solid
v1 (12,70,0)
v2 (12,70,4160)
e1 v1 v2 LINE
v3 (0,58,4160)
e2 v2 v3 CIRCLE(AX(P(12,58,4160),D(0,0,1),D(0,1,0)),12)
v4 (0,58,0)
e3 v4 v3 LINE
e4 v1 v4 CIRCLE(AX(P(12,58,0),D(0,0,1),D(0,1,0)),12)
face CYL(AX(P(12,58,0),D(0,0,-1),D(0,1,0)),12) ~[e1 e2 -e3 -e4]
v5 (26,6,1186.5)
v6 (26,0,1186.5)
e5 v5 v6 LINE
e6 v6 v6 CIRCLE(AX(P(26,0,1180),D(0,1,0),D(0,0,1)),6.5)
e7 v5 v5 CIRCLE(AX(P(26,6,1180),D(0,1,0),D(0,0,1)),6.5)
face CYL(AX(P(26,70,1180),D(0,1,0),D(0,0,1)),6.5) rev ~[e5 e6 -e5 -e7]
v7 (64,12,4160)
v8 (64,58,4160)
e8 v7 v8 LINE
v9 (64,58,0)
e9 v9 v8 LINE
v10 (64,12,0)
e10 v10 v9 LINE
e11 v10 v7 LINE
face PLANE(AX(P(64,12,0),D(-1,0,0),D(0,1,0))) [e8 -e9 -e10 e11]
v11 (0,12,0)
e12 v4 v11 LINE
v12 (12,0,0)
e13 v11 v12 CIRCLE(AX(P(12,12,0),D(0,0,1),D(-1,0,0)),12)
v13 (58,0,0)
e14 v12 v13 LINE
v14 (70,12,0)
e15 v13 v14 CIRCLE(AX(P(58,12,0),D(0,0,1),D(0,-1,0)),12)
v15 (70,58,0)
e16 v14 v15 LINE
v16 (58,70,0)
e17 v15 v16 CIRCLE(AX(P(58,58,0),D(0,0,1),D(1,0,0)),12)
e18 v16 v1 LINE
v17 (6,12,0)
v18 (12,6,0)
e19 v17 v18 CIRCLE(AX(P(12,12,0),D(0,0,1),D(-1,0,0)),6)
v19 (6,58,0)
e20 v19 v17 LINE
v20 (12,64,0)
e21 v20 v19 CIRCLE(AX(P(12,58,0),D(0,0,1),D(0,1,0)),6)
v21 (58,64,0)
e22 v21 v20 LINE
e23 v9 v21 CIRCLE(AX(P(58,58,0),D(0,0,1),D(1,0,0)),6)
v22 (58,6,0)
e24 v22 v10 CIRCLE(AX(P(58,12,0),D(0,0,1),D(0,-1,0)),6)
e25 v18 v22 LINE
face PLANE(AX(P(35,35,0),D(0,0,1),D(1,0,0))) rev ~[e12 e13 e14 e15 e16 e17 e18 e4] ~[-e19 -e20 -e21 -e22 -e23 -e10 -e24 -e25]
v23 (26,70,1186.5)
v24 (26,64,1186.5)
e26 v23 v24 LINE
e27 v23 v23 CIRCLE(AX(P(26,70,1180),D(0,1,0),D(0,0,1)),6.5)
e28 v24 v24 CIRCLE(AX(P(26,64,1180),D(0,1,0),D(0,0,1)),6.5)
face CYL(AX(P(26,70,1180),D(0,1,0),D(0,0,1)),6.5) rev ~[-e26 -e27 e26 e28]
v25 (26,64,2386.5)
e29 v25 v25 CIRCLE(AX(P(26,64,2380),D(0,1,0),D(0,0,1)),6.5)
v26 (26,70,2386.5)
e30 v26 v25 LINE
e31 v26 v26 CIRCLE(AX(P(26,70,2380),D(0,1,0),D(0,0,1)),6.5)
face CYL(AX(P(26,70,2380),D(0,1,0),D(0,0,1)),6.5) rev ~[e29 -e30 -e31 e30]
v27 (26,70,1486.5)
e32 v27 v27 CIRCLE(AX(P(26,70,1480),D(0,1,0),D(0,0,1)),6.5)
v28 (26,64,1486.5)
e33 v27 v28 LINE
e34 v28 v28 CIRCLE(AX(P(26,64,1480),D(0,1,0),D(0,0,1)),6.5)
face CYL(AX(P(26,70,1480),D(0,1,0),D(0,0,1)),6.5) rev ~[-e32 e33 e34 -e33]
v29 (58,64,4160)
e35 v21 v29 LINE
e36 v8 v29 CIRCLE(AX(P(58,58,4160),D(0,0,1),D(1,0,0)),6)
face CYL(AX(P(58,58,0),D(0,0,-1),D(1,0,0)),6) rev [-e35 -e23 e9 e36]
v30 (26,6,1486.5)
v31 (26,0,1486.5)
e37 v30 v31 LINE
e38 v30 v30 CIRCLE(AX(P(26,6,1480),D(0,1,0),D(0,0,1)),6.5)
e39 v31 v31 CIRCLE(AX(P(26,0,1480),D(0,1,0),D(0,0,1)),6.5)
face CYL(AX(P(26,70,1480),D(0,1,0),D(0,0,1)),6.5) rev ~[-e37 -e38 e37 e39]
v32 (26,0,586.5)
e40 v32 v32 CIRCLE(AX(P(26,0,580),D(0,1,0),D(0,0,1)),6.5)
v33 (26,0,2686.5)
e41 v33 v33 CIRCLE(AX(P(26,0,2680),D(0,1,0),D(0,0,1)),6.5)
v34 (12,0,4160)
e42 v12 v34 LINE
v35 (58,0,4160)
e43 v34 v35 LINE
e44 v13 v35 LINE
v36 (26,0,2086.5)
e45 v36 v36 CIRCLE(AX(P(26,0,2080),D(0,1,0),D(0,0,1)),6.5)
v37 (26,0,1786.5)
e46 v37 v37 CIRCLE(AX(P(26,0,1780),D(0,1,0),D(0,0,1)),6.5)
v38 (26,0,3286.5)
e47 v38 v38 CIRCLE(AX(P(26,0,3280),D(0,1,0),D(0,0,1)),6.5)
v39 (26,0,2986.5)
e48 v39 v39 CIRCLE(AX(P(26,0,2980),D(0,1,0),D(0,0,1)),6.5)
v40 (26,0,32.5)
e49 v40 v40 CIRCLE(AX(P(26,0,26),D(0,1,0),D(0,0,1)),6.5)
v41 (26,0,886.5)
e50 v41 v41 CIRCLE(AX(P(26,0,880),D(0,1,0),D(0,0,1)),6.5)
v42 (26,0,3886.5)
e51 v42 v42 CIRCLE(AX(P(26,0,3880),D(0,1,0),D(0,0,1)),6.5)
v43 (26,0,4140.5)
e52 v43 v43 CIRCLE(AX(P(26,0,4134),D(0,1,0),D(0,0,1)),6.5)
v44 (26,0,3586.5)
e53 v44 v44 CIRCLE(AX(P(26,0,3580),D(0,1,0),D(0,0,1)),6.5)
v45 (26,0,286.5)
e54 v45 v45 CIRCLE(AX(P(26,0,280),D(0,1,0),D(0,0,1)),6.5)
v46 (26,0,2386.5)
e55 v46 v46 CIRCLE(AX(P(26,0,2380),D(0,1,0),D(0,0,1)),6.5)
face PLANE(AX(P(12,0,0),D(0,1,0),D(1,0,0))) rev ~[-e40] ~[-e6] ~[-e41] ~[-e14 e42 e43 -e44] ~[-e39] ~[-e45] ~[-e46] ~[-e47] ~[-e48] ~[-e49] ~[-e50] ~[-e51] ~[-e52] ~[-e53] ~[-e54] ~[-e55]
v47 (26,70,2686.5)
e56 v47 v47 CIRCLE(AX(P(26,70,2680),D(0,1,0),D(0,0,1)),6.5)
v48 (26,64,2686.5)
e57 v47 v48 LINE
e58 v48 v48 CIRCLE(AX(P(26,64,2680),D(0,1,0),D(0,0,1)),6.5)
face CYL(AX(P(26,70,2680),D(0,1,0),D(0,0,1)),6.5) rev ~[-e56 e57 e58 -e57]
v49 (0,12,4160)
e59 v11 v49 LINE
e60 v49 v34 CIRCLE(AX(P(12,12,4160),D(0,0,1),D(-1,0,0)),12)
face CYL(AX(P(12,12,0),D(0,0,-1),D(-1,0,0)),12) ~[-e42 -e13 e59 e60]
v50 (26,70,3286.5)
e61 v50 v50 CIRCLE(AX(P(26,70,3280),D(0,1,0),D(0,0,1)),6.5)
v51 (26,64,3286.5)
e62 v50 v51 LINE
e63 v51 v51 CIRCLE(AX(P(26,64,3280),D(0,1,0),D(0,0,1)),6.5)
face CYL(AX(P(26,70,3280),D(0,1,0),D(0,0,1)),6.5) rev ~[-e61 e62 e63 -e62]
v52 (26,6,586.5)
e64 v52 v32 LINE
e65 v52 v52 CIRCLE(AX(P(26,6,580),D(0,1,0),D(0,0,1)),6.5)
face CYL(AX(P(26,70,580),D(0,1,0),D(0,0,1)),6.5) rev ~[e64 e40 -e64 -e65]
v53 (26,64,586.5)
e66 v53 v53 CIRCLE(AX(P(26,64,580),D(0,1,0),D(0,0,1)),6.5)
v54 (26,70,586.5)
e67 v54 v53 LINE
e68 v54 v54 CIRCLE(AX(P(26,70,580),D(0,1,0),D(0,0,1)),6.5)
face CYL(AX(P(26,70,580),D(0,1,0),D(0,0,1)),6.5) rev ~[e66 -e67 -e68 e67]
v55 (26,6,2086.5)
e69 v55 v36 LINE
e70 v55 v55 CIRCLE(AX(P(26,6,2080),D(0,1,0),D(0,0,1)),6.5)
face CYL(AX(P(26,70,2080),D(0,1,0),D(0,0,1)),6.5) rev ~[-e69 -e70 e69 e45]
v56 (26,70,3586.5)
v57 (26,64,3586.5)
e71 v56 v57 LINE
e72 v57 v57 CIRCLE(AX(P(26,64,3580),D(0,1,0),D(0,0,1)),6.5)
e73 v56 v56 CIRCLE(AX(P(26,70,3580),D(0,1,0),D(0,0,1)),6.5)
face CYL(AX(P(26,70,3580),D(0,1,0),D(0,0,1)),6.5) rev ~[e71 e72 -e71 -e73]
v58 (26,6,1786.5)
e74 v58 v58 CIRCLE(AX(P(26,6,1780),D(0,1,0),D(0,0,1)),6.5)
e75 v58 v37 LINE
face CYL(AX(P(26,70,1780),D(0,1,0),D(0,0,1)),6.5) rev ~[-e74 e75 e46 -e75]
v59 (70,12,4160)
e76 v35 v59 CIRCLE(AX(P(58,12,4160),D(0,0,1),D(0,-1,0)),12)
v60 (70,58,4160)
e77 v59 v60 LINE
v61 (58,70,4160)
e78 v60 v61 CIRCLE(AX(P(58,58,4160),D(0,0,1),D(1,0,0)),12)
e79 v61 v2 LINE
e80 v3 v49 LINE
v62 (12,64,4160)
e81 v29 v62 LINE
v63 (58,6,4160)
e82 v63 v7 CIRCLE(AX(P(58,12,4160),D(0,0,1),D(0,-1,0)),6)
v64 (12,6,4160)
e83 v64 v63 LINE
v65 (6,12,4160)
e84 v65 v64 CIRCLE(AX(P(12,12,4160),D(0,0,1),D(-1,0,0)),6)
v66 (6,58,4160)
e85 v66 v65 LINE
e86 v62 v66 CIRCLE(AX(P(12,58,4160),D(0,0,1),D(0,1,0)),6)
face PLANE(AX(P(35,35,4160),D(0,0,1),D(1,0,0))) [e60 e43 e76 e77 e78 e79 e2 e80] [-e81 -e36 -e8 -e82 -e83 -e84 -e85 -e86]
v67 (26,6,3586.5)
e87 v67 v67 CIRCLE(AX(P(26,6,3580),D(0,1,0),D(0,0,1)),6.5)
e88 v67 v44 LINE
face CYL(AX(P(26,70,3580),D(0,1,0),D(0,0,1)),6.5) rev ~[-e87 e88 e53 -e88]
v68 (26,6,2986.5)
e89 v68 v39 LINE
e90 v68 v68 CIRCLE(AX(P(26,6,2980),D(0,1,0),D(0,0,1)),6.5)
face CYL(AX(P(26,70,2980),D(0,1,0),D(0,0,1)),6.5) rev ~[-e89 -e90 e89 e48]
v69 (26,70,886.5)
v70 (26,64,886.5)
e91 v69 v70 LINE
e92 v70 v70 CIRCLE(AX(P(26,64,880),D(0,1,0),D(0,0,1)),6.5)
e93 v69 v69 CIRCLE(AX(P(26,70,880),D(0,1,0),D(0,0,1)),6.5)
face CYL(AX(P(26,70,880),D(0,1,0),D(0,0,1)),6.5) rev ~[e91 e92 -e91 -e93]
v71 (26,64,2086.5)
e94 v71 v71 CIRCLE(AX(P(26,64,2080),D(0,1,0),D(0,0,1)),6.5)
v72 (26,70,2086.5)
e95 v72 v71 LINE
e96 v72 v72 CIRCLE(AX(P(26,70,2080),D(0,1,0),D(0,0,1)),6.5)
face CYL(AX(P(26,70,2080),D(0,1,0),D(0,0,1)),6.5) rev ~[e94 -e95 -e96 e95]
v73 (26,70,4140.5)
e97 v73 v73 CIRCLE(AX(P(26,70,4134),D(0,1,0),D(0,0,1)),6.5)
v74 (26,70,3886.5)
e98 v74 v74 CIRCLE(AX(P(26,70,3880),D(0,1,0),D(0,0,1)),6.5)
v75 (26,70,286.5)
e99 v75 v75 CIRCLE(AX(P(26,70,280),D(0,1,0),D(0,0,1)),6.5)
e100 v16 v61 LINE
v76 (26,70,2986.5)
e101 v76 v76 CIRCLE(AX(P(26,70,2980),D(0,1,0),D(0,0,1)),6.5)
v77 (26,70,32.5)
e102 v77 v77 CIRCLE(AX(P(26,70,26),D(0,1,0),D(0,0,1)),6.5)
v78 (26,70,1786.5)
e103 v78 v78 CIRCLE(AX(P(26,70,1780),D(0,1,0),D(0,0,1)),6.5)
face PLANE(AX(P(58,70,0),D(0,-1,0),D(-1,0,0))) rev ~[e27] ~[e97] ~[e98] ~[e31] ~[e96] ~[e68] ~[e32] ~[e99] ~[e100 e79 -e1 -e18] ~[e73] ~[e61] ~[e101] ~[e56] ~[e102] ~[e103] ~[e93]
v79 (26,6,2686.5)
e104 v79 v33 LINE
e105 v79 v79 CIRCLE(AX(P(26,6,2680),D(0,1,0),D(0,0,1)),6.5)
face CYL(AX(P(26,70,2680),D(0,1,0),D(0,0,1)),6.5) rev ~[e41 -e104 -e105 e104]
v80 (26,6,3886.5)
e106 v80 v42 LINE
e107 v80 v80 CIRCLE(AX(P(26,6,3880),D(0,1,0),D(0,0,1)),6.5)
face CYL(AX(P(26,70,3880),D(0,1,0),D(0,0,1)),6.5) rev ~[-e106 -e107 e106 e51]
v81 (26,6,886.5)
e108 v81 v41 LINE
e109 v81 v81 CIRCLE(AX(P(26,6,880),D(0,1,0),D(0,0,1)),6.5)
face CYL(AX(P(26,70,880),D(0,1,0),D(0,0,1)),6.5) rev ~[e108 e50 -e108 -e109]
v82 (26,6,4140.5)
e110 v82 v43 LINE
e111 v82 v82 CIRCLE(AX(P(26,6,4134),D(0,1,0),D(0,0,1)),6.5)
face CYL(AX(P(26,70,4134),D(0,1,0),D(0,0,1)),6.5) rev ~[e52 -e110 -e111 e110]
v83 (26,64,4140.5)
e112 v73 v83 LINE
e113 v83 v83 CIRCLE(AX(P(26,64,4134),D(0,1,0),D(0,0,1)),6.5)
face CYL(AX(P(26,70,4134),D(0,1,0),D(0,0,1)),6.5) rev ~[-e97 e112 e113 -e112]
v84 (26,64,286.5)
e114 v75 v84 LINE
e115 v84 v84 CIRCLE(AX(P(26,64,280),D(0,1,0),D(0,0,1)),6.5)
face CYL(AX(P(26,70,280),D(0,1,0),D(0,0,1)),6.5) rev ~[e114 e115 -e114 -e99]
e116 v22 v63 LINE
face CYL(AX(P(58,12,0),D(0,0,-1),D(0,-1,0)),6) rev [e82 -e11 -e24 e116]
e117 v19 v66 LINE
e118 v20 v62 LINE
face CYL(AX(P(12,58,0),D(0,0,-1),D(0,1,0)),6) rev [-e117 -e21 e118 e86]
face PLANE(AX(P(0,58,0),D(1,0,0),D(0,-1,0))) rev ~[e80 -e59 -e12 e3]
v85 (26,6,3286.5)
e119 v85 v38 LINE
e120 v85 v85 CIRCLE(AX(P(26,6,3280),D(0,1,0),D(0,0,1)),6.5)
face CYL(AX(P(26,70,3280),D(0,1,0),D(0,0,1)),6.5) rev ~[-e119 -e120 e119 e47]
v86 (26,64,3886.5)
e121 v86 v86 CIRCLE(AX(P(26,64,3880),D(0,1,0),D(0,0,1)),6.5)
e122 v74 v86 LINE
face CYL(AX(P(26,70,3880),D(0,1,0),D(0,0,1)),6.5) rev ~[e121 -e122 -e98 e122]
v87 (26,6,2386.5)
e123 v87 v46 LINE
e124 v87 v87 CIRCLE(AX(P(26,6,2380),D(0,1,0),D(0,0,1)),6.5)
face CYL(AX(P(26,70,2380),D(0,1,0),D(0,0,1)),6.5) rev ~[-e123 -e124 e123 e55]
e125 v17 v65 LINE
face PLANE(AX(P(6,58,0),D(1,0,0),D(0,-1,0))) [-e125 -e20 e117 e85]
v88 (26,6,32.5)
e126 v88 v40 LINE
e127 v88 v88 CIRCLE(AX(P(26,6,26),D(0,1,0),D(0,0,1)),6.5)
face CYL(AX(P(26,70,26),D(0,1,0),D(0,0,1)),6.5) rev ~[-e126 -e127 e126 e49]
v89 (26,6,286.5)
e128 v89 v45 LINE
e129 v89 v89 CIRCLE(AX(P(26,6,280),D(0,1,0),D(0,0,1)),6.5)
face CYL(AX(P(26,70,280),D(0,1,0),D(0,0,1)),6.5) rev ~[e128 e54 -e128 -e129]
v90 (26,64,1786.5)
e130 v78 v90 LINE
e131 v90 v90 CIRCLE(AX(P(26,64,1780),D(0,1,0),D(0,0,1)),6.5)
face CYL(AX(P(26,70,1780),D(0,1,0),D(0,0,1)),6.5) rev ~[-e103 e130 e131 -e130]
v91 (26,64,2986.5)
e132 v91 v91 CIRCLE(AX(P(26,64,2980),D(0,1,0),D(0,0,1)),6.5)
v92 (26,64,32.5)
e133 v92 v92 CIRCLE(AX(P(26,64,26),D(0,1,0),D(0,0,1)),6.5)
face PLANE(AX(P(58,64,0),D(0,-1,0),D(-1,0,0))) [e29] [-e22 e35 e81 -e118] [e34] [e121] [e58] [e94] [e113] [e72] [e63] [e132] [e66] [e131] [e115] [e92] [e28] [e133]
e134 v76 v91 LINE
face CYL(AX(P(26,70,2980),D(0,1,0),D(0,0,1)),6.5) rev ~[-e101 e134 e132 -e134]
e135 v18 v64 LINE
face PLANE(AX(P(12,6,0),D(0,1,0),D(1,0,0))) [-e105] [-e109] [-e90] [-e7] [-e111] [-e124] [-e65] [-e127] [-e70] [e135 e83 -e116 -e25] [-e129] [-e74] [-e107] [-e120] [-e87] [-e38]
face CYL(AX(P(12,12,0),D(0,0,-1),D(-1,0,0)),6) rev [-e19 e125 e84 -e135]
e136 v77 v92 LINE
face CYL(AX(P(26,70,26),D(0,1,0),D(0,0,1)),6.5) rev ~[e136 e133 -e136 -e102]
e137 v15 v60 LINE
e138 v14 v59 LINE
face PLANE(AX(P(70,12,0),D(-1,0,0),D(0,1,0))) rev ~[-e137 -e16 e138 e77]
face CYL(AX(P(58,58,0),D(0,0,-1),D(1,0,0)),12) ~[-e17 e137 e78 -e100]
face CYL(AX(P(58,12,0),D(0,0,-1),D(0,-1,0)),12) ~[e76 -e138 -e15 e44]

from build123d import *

# Parameters (mm, degrees)
BOSS_EXTRUDE1_DEPTH = 4160
SKETCH2_R           = 6.5
CUT_EXTRUDE1_DEPTH  = 4162.177717906
SKETCH3_R           = 6.5
CUT_EXTRUDE2_DEPTH  = 4162.177717906


with BuildPart() as part:
    # Sketch1 → Boss-Extrude1 (new body)
    with BuildSketch(Plane.XY):
        with BuildLine():
            Line((12, 0), (58, 0))
            ThreePointArc((58, 0), (66.485281374, 3.514718626), (70, 12))
            Line((70, 12), (70, 58))
            ThreePointArc((70, 58), (66.485281374, 66.485281374), (58, 70))
            Line((58, 70), (12, 70))
            ThreePointArc((12, 70), (3.514718626, 66.485281374), (0, 58))
            Line((0, 58), (0, 12))
            ThreePointArc((0, 12), (3.514718626, 3.514718626), (12, 0))
        make_face()
        with BuildLine():
            Line((12, 6), (58, 6))
            ThreePointArc((58, 6), (62.242640687, 7.757359313), (64, 12))
            Line((64, 12), (64, 58))
            ThreePointArc((64, 58), (62.242640687, 62.242640687), (58, 64))
            Line((58, 64), (12, 64))
            ThreePointArc((12, 64), (7.757359313, 62.242640687), (6, 58))
            Line((6, 58), (6, 12))
            ThreePointArc((6, 12), (7.757359313, 7.757359313), (12, 6))
        make_face(mode=Mode.SUBTRACT)
    extrude(amount=BOSS_EXTRUDE1_DEPTH)

    # Sketch2 → Cut-Extrude1 (cut, through all)
    with BuildSketch(Plane(origin=(0, 70, 0), x_dir=(1, 0, 0), z_dir=(0, 1, 0))):
        with Locations(Location((26, -280, 0), (0, 0, 270))):
            Circle(SKETCH2_R)
        with Locations(Location((26, -580, 0), (0, 0, 270))):
            Circle(SKETCH2_R)
        with Locations(Location((26, -880, 0), (0, 0, 270))):
            Circle(SKETCH2_R)
        with Locations(Location((26, -1180, 0), (0, 0, 270))):
            Circle(SKETCH2_R)
        with Locations(Location((26, -1480, 0), (0, 0, 270))):
            Circle(SKETCH2_R)
        with Locations(Location((26, -1780, 0), (0, 0, 270))):
            Circle(SKETCH2_R)
        with Locations(Location((26, -2080, 0), (0, 0, 270))):
            Circle(SKETCH2_R)
        with Locations(Location((26, -2380, 0), (0, 0, 270))):
            Circle(SKETCH2_R)
        with Locations(Location((26, -2680, 0), (0, 0, 270))):
            Circle(SKETCH2_R)
        with Locations(Location((26, -2980, 0), (0, 0, 270))):
            Circle(SKETCH2_R)
        with Locations(Location((26, -3280, 0), (0, 0, 270))):
            Circle(SKETCH2_R)
        with Locations(Location((26, -3580, 0), (0, 0, 270))):
            Circle(SKETCH2_R)
        with Locations(Location((26, -3880, 0), (0, 0, 270))):
            Circle(SKETCH2_R)
    extrude(amount=-CUT_EXTRUDE1_DEPTH, mode=Mode.SUBTRACT)

    # Sketch3 → Cut-Extrude2 (cut, through all)
    with BuildSketch(Plane(origin=(0, 70, 0), x_dir=(1, 0, 0), z_dir=(0, 1, 0))):
        with Locations(Location((26, -26, 0), (0, 0, 270))):
            Circle(SKETCH3_R)
        with Locations(Location((26, -4134, 0), (0, 0, 270))):
            Circle(SKETCH3_R)
    extrude(amount=-CUT_EXTRUDE2_DEPTH, mode=Mode.SUBTRACT)


solid = part.part
